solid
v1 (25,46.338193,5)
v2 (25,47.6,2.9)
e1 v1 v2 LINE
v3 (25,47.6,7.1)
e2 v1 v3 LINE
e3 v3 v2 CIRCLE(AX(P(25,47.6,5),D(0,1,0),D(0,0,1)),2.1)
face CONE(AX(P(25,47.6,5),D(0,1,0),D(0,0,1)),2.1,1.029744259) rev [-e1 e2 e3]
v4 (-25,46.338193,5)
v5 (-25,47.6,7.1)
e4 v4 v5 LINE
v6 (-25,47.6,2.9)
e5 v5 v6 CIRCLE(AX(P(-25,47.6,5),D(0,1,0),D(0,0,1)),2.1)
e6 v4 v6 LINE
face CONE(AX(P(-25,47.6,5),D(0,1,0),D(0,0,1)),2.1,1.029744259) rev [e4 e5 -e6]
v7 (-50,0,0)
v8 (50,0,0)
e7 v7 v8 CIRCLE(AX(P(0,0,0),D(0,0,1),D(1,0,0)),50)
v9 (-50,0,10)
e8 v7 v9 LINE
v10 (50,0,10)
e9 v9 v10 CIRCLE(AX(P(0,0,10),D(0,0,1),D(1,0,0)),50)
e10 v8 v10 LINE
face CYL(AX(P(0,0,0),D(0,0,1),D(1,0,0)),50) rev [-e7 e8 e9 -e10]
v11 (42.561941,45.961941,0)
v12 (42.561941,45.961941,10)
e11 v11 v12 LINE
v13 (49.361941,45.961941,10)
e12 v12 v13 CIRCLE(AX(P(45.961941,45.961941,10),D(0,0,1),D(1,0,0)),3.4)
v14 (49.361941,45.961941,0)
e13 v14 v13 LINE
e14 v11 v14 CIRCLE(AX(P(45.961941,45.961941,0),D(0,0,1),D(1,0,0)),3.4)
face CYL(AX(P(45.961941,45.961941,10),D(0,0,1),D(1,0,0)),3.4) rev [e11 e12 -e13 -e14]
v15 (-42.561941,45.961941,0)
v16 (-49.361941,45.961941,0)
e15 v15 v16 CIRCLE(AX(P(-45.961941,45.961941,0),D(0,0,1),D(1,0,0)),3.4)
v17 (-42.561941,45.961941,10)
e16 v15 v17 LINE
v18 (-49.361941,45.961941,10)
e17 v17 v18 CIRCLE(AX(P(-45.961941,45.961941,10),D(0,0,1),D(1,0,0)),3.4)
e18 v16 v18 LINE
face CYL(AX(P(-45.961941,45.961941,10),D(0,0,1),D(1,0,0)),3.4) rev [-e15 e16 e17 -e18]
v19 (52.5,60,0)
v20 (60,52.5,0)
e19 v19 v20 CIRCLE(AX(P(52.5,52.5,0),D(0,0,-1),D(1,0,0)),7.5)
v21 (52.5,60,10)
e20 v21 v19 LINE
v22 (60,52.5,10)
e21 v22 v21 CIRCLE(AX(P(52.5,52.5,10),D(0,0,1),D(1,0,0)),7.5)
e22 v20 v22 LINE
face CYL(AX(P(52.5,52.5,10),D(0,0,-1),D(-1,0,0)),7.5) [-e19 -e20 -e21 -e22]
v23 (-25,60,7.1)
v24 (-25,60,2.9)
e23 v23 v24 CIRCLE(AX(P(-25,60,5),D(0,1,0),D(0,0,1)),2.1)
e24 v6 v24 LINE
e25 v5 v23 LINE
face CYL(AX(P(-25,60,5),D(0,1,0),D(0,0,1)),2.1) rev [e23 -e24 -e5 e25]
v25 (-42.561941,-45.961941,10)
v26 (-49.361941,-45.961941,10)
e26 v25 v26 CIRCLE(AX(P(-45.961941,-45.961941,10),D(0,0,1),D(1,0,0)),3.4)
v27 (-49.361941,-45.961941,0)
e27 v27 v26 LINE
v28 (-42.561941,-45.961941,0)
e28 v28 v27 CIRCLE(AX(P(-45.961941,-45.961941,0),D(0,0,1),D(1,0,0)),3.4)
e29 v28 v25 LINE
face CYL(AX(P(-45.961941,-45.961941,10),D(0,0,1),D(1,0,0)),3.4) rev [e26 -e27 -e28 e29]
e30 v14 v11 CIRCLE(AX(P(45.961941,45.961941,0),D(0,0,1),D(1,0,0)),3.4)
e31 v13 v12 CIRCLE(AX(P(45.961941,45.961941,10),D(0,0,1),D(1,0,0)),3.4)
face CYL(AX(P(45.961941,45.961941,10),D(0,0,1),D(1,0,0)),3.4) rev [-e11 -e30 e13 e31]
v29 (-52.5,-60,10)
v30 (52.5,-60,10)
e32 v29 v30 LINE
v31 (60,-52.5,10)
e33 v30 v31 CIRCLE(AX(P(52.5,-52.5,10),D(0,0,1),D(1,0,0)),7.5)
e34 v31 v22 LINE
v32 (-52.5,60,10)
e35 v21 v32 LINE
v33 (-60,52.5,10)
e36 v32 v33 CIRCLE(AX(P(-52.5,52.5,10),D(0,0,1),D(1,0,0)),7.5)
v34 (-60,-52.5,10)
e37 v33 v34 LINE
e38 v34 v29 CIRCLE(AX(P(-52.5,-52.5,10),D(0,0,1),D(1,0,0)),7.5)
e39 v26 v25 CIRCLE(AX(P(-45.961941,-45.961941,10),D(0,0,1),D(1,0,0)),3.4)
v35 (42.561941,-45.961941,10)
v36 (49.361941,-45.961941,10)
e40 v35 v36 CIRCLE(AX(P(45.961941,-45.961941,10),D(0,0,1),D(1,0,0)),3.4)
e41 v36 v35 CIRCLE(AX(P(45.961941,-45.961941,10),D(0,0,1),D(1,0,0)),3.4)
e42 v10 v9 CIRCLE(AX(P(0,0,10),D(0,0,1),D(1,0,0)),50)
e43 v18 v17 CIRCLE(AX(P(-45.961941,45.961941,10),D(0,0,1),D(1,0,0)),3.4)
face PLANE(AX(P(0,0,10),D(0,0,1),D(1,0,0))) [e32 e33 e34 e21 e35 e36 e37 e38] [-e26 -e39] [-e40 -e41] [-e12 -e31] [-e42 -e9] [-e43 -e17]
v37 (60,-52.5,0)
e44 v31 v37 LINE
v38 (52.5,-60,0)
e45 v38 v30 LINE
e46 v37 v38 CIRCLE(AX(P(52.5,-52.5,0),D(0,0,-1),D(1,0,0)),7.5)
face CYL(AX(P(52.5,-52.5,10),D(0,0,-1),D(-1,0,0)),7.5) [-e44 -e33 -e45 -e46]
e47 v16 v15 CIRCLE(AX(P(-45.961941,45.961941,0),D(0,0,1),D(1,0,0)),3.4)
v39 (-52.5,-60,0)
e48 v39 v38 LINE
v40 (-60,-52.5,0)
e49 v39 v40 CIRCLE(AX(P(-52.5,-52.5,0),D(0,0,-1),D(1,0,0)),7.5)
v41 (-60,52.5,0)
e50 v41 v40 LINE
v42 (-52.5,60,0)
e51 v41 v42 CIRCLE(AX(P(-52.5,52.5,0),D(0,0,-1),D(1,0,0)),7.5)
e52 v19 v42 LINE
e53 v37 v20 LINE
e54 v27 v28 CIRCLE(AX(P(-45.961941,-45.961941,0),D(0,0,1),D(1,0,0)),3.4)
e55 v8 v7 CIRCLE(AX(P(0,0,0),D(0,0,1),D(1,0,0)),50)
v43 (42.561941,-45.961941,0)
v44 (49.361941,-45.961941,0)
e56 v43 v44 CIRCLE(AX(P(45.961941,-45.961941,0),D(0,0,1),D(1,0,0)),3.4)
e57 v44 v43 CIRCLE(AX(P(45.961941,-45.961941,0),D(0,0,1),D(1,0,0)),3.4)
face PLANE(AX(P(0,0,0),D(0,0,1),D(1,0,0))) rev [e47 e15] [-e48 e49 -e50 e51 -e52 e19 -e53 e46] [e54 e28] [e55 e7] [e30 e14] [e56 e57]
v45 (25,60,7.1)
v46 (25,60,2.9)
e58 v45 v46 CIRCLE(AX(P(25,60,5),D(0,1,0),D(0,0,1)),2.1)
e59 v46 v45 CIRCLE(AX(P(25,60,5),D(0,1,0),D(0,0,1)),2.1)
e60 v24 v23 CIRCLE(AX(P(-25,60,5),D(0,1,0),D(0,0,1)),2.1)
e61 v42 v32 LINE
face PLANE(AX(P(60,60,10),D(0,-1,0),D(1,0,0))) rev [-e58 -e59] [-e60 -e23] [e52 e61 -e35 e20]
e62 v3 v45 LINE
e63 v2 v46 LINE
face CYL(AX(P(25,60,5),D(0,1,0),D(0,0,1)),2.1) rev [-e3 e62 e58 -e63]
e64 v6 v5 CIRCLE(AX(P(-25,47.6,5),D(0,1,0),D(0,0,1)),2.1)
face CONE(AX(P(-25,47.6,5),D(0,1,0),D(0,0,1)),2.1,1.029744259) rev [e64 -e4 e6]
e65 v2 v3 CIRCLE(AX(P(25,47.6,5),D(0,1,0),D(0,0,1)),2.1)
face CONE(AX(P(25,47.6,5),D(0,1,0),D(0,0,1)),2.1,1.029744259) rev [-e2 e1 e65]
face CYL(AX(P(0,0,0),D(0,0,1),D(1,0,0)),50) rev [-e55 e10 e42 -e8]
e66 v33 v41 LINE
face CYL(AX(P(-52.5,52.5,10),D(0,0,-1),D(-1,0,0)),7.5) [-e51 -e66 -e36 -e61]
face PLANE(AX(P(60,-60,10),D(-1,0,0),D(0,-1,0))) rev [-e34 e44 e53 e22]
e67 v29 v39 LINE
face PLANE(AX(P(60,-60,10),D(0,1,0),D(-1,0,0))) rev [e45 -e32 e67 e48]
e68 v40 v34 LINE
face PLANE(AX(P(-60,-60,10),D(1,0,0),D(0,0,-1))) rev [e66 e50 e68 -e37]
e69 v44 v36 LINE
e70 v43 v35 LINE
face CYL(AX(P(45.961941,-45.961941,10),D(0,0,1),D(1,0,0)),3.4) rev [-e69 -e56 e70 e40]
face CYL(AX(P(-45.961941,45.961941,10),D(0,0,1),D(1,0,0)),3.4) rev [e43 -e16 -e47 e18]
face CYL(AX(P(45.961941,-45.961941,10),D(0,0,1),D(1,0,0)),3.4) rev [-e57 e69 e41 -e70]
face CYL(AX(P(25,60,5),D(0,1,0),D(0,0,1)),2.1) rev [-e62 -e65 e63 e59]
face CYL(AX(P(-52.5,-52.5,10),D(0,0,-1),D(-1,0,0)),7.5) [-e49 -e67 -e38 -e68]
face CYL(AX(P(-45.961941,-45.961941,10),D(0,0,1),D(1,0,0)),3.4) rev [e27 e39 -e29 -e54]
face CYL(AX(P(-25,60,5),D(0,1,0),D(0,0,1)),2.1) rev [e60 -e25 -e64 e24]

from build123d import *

# Parameters (mm, degrees)
SKETCH1_W             = 120
SKETCH1_H             = 120
BOSS_EXTRUDE1_DEPTH   = 10
FILLET1_R             = 7.5
M5_TAPPED_HOLE1_D     = 4.2
M5_TAPPED_HOLE1_DEPTH = 12.4
M5_TAPPED_HOLE1_TIP   = 1.2618073
SKETCH4_R             = 50
CUT_EXTRUDE1_DEPTH    = 10
M8_TAPPED_HOLE1_D     = 6.8
M8_TAPPED_HOLE1_DEPTH = 19.75
M8_TAPPED_HOLE1_TIP   = 2.042926105


with BuildPart() as part:
    # Sketch1 → Boss-Extrude1 (new body)
    with BuildSketch(Plane.XY):
        Rectangle(SKETCH1_W, SKETCH1_H)
    extrude(amount=BOSS_EXTRUDE1_DEPTH)

    # Fillet1
    fillet1_edges = [part.edges().sort_by_distance(p)[0] for p in [
        (-60, 60, 5),
        (60, 60, 5),
        (60, -60, 5),
        (-60, -60, 5),
    ]]
    fillet(fillet1_edges, radius=FILLET1_R)

    # M5 Tapped Hole1
    with Locations(Plane(origin=(0, 60, 0), x_dir=(1, 0, 0), z_dir=(0, 1, 0))):
        with Locations((-25, -5), (25, -5)):
            Hole(M5_TAPPED_HOLE1_D / 2, depth=M5_TAPPED_HOLE1_DEPTH)
            with Locations((0, 0, -(M5_TAPPED_HOLE1_DEPTH + M5_TAPPED_HOLE1_TIP / 2))):  # 118° drill point
                Cone(0, M5_TAPPED_HOLE1_D / 2, M5_TAPPED_HOLE1_TIP, mode=Mode.SUBTRACT)

    # Sketch4 → Cut-Extrude1 (cut)
    with BuildSketch(Plane.XY.offset(10)):
        Circle(SKETCH4_R)
    extrude(amount=-CUT_EXTRUDE1_DEPTH, mode=Mode.SUBTRACT)

    # M8 Tapped Hole1
    with Locations(Plane.XY.offset(10)):
        with Locations((-45.961940777, 45.961940777), (45.961940777, 45.961940777), (45.961940777, -45.961940777), (-45.961940777, -45.961940777)):
            Hole(M8_TAPPED_HOLE1_D / 2, depth=M8_TAPPED_HOLE1_DEPTH)
            with Locations((0, 0, -(M8_TAPPED_HOLE1_DEPTH + M8_TAPPED_HOLE1_TIP / 2))):  # 118° drill point
                Cone(0, M8_TAPPED_HOLE1_D / 2, M8_TAPPED_HOLE1_TIP, mode=Mode.SUBTRACT)


solid = part.part
